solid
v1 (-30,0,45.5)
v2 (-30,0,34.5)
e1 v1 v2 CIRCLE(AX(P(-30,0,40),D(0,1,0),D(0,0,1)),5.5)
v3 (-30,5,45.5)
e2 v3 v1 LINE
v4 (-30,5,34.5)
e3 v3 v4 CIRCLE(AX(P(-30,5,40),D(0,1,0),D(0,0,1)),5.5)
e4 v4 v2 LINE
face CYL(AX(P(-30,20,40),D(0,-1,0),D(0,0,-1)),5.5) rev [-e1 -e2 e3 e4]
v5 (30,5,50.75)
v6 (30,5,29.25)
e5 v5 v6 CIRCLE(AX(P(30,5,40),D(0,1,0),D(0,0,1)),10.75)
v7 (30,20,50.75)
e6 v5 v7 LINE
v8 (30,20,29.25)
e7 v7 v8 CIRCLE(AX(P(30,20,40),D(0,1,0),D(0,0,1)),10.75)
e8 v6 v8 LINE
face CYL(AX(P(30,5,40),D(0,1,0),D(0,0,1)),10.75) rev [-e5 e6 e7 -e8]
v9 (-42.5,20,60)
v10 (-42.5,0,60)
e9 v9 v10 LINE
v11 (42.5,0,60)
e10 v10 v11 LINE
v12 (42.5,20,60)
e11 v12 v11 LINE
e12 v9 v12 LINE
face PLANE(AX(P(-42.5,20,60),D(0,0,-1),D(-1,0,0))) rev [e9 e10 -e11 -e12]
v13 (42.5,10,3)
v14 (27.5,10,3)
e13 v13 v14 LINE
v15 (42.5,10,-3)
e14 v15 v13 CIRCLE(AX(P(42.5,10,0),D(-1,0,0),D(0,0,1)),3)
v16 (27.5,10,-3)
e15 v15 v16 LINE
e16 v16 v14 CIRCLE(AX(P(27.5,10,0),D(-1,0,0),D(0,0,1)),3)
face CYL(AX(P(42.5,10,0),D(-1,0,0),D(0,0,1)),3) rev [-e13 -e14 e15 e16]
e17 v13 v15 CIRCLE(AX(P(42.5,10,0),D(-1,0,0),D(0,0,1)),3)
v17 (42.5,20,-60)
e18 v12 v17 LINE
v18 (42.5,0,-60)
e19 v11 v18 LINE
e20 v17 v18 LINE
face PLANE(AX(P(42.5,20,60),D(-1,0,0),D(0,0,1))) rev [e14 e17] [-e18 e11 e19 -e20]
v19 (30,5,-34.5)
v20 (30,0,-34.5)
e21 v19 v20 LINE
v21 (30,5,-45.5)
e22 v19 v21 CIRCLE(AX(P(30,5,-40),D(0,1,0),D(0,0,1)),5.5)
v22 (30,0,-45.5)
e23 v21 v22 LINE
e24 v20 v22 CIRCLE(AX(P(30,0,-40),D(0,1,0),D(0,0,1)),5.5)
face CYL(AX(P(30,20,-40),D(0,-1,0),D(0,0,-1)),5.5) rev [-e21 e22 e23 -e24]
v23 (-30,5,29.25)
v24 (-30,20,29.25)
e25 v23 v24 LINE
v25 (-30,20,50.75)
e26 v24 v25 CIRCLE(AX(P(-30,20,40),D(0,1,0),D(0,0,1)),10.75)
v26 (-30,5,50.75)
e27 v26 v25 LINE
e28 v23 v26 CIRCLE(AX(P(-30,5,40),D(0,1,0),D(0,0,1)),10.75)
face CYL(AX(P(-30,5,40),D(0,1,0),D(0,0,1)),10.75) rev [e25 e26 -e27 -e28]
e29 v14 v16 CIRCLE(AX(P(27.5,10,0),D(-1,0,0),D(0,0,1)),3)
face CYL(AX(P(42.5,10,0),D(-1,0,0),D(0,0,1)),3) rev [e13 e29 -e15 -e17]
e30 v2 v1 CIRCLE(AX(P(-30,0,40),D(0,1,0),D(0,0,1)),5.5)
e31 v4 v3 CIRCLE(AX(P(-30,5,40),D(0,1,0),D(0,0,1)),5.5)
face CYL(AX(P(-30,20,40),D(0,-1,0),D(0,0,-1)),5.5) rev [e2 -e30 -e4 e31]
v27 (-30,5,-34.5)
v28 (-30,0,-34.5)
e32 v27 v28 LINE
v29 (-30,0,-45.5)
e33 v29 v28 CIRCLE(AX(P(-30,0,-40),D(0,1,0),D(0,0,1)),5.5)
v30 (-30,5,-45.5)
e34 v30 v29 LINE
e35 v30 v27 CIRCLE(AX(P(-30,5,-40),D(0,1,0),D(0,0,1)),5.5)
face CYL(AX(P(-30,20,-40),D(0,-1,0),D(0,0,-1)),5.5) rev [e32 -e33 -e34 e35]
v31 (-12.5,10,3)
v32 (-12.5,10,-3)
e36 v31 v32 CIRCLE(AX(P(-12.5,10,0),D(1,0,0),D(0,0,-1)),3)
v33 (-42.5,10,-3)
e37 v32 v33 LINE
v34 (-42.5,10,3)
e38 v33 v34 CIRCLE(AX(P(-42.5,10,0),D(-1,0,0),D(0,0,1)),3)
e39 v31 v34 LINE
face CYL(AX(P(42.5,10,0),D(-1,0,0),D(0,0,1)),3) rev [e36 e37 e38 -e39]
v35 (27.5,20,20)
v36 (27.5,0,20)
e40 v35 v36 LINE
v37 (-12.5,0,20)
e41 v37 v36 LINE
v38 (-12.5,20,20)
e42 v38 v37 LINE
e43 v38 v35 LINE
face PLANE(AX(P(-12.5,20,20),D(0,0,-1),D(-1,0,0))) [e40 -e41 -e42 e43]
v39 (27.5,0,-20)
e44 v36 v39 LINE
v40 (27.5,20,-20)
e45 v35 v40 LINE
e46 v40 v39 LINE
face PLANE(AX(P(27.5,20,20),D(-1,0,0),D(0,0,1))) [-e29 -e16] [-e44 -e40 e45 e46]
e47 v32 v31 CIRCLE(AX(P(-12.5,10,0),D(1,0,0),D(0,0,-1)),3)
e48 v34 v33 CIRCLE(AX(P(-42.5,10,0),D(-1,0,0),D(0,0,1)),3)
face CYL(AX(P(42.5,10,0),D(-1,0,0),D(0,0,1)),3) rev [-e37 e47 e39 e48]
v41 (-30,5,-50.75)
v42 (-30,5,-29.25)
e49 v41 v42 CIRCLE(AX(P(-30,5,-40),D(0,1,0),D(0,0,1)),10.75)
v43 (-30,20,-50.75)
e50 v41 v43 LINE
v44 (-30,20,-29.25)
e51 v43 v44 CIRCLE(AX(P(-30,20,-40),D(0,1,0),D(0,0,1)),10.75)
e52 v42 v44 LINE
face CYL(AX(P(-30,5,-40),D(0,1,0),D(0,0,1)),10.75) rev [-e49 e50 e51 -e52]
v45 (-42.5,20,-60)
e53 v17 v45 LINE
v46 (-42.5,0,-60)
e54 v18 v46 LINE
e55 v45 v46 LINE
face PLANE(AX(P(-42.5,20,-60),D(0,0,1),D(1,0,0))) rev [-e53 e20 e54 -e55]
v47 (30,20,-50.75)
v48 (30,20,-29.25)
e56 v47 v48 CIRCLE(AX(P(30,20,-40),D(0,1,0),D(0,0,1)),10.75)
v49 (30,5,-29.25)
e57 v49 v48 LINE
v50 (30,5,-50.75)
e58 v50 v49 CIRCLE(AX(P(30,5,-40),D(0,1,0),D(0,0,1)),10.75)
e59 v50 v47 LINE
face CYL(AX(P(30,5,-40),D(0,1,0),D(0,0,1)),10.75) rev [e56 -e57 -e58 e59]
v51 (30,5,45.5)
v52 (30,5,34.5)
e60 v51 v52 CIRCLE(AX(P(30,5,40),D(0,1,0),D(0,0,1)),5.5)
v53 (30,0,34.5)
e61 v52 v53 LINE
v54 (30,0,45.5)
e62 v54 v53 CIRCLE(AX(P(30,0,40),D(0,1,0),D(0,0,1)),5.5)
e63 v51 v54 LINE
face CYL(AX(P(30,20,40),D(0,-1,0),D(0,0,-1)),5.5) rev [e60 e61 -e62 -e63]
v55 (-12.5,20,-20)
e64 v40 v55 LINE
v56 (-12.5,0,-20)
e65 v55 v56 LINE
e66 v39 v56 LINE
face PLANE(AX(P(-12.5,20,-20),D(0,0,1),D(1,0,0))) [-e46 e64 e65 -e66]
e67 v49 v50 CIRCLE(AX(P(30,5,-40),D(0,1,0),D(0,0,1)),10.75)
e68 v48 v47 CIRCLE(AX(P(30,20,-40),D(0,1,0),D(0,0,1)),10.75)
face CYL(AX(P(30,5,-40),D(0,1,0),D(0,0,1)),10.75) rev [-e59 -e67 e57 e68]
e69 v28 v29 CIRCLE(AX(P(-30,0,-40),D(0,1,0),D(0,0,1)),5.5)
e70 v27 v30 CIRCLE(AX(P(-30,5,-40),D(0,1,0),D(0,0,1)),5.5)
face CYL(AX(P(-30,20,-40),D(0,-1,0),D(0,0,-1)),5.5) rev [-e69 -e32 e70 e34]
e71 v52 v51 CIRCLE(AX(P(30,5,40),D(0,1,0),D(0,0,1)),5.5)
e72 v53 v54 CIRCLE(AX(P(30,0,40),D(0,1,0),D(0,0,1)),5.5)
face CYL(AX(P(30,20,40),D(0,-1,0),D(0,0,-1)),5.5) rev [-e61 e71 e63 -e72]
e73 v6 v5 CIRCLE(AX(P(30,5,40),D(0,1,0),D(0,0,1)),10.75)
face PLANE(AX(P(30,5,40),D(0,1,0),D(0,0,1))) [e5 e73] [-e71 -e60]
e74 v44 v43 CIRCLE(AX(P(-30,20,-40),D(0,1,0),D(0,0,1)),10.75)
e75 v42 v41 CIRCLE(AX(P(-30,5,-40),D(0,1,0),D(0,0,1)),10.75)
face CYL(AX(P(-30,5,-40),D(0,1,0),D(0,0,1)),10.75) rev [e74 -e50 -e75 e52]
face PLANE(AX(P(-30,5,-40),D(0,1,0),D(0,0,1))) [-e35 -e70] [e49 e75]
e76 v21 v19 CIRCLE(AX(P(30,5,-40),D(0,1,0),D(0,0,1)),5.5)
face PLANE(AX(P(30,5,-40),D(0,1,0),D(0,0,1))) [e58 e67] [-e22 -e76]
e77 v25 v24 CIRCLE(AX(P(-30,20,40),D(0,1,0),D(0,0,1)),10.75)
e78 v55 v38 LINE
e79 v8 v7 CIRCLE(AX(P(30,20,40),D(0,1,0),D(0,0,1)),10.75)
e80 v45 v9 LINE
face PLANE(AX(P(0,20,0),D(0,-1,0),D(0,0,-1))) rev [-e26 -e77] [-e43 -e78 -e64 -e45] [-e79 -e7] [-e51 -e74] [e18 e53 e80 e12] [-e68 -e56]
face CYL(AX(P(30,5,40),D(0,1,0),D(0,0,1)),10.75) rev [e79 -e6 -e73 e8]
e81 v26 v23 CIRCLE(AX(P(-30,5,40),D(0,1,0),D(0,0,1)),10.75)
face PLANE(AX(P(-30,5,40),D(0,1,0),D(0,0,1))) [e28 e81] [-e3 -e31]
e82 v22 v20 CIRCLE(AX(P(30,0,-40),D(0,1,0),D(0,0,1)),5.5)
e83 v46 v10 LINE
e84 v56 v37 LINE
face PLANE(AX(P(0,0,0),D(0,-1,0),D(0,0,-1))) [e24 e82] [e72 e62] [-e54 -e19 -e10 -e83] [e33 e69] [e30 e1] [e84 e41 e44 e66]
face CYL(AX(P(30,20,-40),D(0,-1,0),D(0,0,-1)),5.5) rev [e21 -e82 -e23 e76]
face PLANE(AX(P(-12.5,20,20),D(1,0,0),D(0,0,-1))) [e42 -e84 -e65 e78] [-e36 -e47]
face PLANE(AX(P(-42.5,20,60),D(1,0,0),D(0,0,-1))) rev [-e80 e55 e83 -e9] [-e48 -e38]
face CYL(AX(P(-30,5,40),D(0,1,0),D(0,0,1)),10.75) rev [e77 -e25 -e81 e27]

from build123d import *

# Parameters (mm, degrees)
SKETCH1_W           = 85
SKETCH1_H           = 120
SKETCH1_R           = 5.5
SKETCH1_W_2         = 40
SKETCH1_H_2         = 40
BOSS_EXTRUDE1_DEPTH = 20
SKETCH2_R           = 10.75
CUT_EXTRUDE1_DEPTH  = 15
SKETCH3_R           = 3
CUT_EXTRUDE2_DEPTH  = 106.948100502


with BuildPart() as part:
    # Sketch1 → Boss-Extrude1 (new body)
    with BuildSketch(Plane(origin=(0, 0, 0), x_dir=(1, 0, 0), z_dir=(0, 1, 0))):
        Rectangle(SKETCH1_W, SKETCH1_H)
        with Locations(Location((-30, 40, 0), (0, 0, 270))):
            Circle(SKETCH1_R, mode=Mode.SUBTRACT)
        with Locations(Location((30, 40, 0), (0, 0, 270))):
            Circle(SKETCH1_R, mode=Mode.SUBTRACT)
        with Locations(Location((30, -40, 0), (0, 0, 270))):
            Circle(SKETCH1_R, mode=Mode.SUBTRACT)
        with Locations(Location((-30, -40, 0), (0, 0, 270))):
            Circle(SKETCH1_R, mode=Mode.SUBTRACT)
        with Locations((7.5, 0)):
            Rectangle(SKETCH1_W_2, SKETCH1_H_2, mode=Mode.SUBTRACT)
    extrude(amount=BOSS_EXTRUDE1_DEPTH)

    # Sketch2 → Cut-Extrude1 (cut)
    with BuildSketch(Plane(origin=(0, 20, 0), x_dir=(1, 0, 0), z_dir=(0, 1, 0))):
        with Locations(Location((30, 40, 0), (0, 0, 270))):
            Circle(SKETCH2_R)
        with Locations(Location((-30, 40, 0), (0, 0, 270))):
            Circle(SKETCH2_R)
        with Locations(Location((-30, -40, 0), (0, 0, 270))):
            Circle(SKETCH2_R)
        with Locations(Location((30, -40, 0), (0, 0, 270))):
            Circle(SKETCH2_R)
    extrude(amount=-CUT_EXTRUDE1_DEPTH, mode=Mode.SUBTRACT)

    # Sketch3 → Cut-Extrude2 (cut, through all)
    with BuildSketch(Plane.ZY.offset(42.5)):
        with Locations((0, 10)):
            Circle(SKETCH3_R)
    extrude(amount=-CUT_EXTRUDE2_DEPTH, mode=Mode.SUBTRACT)


solid = part.part
